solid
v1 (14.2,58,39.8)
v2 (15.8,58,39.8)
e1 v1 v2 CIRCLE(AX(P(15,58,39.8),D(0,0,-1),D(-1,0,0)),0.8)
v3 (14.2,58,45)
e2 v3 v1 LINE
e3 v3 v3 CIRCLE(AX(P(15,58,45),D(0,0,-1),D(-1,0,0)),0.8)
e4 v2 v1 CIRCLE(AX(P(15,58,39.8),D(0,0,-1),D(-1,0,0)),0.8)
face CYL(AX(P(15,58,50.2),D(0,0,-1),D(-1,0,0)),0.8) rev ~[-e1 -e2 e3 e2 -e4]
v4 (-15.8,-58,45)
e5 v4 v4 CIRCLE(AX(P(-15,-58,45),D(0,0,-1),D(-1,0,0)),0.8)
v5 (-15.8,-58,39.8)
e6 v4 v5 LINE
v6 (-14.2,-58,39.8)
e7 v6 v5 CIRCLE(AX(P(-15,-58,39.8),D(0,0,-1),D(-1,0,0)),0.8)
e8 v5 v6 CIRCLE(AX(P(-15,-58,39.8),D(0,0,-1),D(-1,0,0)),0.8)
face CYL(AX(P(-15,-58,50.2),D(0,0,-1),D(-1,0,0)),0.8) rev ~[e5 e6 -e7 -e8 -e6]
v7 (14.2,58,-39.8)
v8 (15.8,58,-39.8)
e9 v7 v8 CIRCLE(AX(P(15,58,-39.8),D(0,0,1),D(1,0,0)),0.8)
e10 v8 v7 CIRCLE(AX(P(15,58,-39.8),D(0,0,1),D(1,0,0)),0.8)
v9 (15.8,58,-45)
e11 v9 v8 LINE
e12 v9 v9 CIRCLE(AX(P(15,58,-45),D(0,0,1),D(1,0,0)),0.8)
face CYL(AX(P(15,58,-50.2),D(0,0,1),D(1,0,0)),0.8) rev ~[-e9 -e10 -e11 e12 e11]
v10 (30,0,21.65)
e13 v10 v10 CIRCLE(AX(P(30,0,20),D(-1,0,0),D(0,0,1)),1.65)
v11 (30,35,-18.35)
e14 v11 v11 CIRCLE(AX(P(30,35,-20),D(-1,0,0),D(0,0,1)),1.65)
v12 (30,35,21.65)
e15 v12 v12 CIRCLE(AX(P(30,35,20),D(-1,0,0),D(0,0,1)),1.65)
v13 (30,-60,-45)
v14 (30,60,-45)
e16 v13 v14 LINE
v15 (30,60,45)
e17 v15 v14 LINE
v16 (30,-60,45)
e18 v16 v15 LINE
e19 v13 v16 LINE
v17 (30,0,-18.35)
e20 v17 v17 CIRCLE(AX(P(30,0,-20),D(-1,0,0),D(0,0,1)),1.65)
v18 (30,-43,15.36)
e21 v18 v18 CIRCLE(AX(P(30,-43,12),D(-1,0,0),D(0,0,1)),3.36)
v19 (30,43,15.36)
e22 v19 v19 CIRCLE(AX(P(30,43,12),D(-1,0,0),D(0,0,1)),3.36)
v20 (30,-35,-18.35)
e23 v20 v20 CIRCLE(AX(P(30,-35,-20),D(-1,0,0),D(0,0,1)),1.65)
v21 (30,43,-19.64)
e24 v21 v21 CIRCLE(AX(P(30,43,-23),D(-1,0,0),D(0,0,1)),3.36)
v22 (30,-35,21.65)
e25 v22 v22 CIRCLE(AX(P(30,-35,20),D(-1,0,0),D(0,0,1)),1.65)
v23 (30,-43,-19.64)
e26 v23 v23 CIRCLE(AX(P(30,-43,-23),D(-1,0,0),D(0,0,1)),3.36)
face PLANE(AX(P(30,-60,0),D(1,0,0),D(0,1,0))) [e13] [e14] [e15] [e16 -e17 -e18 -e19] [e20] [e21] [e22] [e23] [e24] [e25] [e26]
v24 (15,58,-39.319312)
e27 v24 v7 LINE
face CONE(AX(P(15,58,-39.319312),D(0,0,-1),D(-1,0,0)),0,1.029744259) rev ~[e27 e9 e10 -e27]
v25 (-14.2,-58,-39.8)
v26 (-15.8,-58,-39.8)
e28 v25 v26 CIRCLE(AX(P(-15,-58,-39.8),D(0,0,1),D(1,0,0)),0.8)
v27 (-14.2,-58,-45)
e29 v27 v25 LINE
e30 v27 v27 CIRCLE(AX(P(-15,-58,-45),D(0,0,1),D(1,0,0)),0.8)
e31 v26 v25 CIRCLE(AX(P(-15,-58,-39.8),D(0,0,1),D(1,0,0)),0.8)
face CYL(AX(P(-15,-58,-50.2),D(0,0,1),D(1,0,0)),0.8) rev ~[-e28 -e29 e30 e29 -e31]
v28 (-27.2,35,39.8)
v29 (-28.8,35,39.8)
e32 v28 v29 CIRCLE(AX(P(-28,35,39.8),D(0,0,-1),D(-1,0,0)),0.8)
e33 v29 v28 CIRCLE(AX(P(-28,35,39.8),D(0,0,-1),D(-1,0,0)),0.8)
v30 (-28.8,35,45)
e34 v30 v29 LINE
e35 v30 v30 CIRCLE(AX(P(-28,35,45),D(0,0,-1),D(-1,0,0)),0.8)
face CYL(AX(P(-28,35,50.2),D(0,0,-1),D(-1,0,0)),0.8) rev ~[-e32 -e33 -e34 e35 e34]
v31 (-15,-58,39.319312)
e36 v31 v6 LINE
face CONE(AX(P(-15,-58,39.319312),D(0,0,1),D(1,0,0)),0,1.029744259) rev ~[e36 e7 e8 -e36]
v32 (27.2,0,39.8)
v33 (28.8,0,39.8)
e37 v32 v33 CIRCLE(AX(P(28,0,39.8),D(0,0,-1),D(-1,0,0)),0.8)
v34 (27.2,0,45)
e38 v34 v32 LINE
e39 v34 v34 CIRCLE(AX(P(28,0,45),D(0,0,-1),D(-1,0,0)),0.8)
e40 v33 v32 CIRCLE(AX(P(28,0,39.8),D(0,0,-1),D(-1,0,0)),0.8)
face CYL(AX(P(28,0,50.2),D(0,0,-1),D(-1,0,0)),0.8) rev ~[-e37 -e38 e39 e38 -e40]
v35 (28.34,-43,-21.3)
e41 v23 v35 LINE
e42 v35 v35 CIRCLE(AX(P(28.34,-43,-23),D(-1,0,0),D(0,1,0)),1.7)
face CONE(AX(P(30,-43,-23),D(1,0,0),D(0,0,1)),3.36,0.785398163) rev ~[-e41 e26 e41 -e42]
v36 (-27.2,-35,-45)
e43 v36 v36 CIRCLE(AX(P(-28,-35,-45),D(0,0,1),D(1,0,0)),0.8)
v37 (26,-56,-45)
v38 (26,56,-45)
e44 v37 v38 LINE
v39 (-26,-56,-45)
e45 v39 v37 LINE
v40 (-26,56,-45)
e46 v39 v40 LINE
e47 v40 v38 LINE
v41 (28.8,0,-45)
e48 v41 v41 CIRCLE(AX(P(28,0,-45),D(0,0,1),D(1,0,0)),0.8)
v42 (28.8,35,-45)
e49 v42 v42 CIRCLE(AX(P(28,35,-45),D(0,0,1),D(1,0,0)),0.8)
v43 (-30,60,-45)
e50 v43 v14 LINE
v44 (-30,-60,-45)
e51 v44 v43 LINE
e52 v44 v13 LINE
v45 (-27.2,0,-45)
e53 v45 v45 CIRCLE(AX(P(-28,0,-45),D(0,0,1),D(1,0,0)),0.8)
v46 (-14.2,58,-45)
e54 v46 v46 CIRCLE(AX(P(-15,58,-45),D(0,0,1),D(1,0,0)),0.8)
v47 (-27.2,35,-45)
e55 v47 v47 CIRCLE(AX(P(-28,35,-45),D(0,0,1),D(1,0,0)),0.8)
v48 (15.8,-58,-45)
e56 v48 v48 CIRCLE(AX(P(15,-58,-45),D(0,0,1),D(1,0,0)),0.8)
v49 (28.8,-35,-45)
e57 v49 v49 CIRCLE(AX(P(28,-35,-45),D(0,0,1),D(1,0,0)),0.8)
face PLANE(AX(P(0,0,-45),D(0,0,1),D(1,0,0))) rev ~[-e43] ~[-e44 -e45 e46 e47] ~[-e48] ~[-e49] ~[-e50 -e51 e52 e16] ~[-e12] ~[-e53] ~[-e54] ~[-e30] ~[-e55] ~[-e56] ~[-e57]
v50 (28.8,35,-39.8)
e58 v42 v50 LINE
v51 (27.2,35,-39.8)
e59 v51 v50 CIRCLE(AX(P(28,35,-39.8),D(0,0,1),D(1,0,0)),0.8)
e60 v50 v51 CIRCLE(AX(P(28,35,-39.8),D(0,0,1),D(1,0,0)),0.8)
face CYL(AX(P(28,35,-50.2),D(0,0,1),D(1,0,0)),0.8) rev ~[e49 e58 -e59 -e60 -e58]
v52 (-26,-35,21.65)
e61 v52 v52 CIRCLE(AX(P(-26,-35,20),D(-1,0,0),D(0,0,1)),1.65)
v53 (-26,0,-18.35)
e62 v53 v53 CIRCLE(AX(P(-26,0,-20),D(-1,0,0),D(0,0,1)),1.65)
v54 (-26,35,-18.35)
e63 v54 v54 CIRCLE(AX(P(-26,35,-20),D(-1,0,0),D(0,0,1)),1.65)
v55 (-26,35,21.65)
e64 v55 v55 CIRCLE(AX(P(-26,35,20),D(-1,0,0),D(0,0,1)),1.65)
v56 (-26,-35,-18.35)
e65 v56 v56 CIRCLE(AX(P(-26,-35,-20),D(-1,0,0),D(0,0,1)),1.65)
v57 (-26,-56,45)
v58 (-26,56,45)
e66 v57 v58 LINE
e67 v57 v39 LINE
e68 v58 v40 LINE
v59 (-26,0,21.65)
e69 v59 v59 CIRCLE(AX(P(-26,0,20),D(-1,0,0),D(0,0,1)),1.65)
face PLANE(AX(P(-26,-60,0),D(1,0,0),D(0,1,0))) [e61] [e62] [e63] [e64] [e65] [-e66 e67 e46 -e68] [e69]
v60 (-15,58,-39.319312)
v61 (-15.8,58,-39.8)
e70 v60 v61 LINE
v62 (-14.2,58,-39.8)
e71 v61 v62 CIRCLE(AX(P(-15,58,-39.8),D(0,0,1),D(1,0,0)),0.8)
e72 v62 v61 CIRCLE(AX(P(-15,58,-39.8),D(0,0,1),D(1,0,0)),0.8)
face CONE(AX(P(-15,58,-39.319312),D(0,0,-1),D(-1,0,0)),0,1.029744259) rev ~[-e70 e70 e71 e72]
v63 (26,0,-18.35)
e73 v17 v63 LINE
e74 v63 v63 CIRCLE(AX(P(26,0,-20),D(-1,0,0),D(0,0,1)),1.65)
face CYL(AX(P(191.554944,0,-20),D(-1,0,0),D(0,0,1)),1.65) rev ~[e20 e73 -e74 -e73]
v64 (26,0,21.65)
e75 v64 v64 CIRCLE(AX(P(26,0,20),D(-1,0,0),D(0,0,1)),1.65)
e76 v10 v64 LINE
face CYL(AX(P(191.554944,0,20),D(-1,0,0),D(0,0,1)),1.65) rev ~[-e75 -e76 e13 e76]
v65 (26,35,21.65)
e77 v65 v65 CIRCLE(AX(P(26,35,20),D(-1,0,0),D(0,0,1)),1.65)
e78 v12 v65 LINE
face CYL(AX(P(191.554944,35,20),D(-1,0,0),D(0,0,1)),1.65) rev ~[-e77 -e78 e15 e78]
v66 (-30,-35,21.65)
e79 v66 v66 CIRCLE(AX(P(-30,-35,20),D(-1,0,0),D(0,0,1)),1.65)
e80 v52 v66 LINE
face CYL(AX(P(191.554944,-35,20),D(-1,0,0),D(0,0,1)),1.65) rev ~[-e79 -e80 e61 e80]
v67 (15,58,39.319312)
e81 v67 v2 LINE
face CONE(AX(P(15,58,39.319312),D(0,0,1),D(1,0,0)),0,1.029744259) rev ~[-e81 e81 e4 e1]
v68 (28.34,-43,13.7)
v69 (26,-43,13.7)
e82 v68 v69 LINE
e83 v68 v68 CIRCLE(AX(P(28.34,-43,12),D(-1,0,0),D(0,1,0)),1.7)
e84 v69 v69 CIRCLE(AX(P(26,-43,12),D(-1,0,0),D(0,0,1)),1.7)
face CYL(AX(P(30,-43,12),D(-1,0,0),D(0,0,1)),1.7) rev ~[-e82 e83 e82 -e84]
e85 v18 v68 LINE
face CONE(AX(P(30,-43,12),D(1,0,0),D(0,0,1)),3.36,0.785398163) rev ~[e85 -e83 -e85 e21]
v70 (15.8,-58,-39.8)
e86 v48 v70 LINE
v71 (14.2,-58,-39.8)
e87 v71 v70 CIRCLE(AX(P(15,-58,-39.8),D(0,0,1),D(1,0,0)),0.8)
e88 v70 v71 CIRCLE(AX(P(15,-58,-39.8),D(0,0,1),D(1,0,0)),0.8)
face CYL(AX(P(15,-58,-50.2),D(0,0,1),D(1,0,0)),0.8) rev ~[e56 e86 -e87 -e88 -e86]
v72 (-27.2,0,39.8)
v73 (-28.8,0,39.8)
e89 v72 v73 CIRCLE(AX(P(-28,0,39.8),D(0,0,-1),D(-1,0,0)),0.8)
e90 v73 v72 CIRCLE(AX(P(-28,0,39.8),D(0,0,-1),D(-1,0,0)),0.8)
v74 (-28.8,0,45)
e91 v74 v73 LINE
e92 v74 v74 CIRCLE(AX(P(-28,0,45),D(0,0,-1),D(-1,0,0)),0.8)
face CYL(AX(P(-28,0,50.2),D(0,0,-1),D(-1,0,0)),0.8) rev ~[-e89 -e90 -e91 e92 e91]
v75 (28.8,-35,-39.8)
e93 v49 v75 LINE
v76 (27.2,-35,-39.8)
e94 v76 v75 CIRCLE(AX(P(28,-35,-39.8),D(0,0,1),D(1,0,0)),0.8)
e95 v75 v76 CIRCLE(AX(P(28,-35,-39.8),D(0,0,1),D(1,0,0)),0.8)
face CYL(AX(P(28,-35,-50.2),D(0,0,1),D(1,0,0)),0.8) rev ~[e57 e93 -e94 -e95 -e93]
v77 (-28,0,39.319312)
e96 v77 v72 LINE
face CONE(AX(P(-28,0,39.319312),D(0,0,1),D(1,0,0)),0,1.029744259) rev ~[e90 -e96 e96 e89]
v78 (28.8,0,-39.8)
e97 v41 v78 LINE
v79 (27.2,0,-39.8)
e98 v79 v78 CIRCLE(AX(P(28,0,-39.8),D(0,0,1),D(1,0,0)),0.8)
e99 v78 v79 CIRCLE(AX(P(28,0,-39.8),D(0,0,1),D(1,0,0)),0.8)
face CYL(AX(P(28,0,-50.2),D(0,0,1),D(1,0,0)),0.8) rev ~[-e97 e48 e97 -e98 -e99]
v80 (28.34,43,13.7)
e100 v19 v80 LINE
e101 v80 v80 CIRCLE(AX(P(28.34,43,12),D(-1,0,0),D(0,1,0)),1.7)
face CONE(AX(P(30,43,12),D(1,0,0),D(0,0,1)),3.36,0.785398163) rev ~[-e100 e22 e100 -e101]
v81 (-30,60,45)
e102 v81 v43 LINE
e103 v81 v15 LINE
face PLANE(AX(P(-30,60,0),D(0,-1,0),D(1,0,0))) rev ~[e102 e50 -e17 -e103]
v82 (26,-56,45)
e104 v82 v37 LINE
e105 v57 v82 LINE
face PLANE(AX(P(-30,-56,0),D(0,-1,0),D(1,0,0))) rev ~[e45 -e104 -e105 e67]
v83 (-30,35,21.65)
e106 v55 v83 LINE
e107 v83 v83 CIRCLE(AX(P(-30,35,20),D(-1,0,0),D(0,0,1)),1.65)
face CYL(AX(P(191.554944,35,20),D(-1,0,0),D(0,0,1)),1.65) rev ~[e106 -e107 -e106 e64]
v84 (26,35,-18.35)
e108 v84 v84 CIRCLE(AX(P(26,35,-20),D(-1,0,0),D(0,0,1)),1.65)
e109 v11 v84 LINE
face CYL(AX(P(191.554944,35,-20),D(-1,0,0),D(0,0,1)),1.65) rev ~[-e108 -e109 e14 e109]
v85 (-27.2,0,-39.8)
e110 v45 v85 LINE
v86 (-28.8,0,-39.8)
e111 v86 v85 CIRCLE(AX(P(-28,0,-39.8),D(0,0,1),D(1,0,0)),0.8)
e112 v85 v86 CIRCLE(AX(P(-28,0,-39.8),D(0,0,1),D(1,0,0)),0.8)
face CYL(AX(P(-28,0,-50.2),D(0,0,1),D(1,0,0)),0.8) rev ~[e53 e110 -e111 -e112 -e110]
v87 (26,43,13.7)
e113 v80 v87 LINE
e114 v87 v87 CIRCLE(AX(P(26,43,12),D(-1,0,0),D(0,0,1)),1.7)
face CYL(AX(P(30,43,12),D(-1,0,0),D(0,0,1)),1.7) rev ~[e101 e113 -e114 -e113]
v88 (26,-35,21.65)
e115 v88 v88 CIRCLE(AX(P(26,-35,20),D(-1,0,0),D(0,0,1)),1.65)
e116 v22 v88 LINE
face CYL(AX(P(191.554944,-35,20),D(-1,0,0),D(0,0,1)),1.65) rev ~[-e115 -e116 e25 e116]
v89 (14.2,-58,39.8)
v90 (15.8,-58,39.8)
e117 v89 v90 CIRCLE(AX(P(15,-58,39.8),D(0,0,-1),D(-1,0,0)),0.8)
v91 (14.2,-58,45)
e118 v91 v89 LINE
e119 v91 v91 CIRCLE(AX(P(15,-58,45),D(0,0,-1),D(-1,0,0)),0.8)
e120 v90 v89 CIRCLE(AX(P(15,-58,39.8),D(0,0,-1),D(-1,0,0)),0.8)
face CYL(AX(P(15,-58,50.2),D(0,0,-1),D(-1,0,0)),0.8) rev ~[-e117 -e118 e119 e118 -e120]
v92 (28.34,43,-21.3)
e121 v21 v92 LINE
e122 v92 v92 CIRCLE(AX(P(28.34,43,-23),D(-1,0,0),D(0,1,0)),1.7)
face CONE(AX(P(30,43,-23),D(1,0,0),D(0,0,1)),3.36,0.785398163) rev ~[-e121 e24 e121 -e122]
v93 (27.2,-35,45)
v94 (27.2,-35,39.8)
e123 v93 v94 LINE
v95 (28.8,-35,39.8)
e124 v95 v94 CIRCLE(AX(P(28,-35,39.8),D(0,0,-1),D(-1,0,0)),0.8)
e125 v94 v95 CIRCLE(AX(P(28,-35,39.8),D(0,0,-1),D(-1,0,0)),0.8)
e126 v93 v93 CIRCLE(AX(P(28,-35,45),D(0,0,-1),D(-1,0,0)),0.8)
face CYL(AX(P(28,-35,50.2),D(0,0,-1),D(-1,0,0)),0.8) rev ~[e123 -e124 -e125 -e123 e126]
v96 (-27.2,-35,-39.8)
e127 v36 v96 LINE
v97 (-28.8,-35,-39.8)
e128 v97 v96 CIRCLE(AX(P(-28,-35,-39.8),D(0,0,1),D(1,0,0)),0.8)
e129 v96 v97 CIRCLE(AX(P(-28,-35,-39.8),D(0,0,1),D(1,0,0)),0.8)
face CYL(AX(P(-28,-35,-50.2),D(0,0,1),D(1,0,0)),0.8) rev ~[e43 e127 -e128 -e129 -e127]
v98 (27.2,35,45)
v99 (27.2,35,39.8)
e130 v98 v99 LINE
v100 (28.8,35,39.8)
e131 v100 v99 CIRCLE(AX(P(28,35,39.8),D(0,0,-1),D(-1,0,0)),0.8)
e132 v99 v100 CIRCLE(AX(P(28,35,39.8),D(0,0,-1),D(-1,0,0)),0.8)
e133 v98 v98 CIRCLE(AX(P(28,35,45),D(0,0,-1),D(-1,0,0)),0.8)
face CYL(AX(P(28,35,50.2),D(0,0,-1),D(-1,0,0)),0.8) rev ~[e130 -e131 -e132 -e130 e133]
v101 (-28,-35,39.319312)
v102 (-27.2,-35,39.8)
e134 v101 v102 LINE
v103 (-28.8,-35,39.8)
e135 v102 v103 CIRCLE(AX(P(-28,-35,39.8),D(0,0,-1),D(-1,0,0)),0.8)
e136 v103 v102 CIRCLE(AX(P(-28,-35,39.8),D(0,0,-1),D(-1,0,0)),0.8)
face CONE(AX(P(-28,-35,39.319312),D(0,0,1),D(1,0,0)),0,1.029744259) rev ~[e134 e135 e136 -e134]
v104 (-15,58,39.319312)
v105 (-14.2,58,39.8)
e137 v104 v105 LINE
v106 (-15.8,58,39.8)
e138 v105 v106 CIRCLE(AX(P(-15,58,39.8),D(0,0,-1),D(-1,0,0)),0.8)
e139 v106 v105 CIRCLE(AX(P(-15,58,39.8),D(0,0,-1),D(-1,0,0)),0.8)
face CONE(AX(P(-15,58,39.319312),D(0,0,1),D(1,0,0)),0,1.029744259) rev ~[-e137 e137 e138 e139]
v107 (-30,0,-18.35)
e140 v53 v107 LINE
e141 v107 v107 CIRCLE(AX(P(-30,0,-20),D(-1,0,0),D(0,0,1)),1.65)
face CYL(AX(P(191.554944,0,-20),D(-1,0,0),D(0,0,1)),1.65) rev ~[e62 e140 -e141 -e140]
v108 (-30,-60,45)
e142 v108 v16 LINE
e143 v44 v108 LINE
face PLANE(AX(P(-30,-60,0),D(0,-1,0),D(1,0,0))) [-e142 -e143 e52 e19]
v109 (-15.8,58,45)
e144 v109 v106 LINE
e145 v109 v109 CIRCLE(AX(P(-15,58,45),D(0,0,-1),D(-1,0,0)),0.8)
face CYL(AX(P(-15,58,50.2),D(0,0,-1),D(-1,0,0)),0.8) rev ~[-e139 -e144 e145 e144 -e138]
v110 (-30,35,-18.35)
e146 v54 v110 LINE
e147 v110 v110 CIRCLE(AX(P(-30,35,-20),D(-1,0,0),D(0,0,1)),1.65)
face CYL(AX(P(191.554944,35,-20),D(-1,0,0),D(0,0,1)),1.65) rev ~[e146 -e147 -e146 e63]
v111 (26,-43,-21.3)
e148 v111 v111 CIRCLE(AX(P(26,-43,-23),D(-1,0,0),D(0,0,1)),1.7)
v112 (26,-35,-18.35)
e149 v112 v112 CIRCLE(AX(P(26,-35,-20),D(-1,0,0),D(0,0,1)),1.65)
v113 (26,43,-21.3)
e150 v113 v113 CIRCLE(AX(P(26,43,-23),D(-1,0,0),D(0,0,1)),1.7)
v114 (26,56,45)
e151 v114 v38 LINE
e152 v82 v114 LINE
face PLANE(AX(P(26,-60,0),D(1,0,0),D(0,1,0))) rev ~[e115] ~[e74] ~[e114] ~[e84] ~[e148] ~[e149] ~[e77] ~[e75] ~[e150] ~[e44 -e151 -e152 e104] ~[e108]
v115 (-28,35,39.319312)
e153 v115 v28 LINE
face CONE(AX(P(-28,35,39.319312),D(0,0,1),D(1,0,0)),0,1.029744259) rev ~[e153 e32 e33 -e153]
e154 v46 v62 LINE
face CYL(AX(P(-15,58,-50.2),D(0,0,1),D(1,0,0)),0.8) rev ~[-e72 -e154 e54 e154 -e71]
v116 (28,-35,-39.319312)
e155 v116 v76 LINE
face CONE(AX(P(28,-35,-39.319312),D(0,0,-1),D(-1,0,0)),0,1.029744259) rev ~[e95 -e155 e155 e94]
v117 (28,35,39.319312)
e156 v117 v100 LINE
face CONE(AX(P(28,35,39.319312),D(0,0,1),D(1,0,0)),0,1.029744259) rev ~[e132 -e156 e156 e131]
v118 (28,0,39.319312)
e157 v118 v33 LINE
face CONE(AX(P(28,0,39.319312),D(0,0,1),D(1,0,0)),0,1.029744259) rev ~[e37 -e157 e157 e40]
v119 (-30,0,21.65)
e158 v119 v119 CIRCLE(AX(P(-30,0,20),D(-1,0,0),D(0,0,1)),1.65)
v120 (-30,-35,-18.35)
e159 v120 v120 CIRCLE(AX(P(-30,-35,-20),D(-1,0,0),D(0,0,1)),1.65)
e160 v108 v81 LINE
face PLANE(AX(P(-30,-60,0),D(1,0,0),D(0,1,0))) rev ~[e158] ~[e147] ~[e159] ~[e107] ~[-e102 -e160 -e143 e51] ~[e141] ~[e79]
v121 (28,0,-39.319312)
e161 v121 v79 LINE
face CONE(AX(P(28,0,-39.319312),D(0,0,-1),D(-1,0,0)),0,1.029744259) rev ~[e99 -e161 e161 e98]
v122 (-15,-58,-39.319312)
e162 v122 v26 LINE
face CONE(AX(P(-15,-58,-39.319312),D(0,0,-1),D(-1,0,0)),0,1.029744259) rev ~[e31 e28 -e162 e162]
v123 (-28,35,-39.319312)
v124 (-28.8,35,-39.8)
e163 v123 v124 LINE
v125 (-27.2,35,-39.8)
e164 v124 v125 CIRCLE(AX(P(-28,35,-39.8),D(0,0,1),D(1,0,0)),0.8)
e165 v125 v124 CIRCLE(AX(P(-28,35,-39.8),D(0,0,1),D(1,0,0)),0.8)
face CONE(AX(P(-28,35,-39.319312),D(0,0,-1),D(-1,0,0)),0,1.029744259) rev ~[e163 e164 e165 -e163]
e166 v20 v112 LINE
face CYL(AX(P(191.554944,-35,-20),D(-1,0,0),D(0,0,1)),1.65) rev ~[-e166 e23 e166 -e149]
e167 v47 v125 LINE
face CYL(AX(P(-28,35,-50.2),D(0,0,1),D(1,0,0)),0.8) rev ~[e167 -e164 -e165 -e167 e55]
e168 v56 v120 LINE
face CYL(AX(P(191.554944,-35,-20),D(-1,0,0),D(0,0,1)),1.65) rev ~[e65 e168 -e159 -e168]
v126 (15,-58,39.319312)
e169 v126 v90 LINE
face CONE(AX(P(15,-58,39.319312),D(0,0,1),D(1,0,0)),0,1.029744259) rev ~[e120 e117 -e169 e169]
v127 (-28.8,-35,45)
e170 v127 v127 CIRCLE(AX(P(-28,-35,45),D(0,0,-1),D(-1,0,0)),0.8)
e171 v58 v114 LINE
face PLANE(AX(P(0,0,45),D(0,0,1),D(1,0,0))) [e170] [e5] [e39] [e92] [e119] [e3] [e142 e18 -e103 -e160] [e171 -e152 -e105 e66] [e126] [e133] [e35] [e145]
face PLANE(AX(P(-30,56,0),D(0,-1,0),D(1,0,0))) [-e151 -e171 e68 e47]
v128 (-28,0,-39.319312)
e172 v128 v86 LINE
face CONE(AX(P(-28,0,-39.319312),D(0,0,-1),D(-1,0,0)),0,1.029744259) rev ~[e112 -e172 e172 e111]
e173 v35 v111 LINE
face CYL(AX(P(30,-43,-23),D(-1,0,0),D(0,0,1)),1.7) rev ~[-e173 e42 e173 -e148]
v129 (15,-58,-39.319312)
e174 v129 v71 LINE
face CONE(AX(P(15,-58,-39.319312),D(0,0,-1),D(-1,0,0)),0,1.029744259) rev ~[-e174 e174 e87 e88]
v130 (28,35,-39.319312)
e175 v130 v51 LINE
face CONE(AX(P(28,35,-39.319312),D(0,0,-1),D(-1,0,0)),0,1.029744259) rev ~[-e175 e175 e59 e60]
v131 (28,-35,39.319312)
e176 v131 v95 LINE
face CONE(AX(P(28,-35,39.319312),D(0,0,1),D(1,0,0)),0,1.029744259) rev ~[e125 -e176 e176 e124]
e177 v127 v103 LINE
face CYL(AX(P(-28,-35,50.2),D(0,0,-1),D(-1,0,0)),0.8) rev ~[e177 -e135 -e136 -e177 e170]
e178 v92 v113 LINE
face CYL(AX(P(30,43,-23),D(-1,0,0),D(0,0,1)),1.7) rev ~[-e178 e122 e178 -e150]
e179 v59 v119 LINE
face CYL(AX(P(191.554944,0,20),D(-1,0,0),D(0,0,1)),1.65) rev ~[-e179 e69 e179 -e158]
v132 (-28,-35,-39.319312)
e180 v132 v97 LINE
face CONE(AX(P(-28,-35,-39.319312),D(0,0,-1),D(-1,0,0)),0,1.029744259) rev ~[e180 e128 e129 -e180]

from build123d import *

# Parameters (mm, degrees)
SKETCH_1_W                   = 60
SKETCH_1_H                   = 120
EXTRUDE_1_DEPTH              = 45
SHELL_1_T                    = -4
HOLE_WIZARD_M2_1_D           = 1.6
HOLE_WIZARD_M2_1_DEPTH       = 5.2
HOLE_WIZARD_M2_1_TIP         = 0.480688495
HOLE_WIZARD_M2_2_D           = 1.6
HOLE_WIZARD_M2_2_DEPTH       = 5.2
HOLE_WIZARD_M2_2_TIP         = 0.480688495
HOLE_WIZARD_M3_1_D           = 3.4
HOLE_WIZARD_M3_1_DEPTH       = 4
HOLE_WIZARD_M3_1_CSINK_D     = 6.72
HOLE_WIZARD_M3_1_CSINK_ANGLE = 90
HOLE_WIZARD_M4_1_D           = 3.3


with BuildPart() as part:
    # 草图1 → 凸台-拉伸1 (new, symmetric)
    with BuildSketch(Plane.XY):
        Rectangle(SKETCH_1_W, SKETCH_1_H)
    extrude(amount=EXTRUDE_1_DEPTH, both=True)

    # 抽壳1
    shell_1_openings = [part.faces().sort_by_distance(p)[0] for p in [
        (0, 0, 45),
        (0, 0, -45),
    ]]
    offset(amount=SHELL_1_T, openings=shell_1_openings, kind=Kind.INTERSECTION)

    # M2 螺纹孔1
    with Locations(Plane.XY.offset(45)):
        with Locations((-15, -58), (-28, 0), (28, 0), (-15, 58), (15, 58), (-28, 35), (28, 35), (28, -35), (-28, -35), (15, -58)):
            Hole(HOLE_WIZARD_M2_1_D / 2, depth=HOLE_WIZARD_M2_1_DEPTH)
            with Locations((0, 0, -(HOLE_WIZARD_M2_1_DEPTH + HOLE_WIZARD_M2_1_TIP / 2))):  # 118° drill point
                Cone(0, HOLE_WIZARD_M2_1_D / 2, HOLE_WIZARD_M2_1_TIP, mode=Mode.SUBTRACT)

    # M2 螺纹孔2
    with Locations(Plane(origin=(0, 0, -45), x_dir=(-1, 0, 0), z_dir=(0, 0, -1))):
        with Locations((28, 0), (-28, 0), (-15, 58), (15, 58), (28, 35), (-28, 35), (-28, -35), (28, -35), (-15, -58), (15, -58)):
            Hole(HOLE_WIZARD_M2_2_D / 2, depth=HOLE_WIZARD_M2_2_DEPTH)
            with Locations((0, 0, -(HOLE_WIZARD_M2_2_DEPTH + HOLE_WIZARD_M2_2_TIP / 2))):  # 118° drill point
                Cone(0, HOLE_WIZARD_M2_2_D / 2, HOLE_WIZARD_M2_2_TIP, mode=Mode.SUBTRACT)

    # M3 六角凹锥坑螺钉的锥形沉头孔1
    with Locations(Plane(origin=(30, 0, 0), x_dir=(0, 0, -1), z_dir=(1, 0, 0))):
        with Locations((-12, 43), (23, 43), (-12, -43), (23, -43)):
            CounterSinkHole(HOLE_WIZARD_M3_1_D / 2, HOLE_WIZARD_M3_1_CSINK_D / 2, depth=HOLE_WIZARD_M3_1_DEPTH, counter_sink_angle=HOLE_WIZARD_M3_1_CSINK_ANGLE)

    # M4 螺纹孔1 (through all)
    with Locations(Plane(origin=(30, 0, 0), x_dir=(0, 0, -1), z_dir=(1, 0, 0))):
        with Locations((20, 35), (-20, -35), (-20, 35), (20, -35), (-20, 0), (20, 0)):
            Hole(HOLE_WIZARD_M4_1_D / 2)


solid = part.part
